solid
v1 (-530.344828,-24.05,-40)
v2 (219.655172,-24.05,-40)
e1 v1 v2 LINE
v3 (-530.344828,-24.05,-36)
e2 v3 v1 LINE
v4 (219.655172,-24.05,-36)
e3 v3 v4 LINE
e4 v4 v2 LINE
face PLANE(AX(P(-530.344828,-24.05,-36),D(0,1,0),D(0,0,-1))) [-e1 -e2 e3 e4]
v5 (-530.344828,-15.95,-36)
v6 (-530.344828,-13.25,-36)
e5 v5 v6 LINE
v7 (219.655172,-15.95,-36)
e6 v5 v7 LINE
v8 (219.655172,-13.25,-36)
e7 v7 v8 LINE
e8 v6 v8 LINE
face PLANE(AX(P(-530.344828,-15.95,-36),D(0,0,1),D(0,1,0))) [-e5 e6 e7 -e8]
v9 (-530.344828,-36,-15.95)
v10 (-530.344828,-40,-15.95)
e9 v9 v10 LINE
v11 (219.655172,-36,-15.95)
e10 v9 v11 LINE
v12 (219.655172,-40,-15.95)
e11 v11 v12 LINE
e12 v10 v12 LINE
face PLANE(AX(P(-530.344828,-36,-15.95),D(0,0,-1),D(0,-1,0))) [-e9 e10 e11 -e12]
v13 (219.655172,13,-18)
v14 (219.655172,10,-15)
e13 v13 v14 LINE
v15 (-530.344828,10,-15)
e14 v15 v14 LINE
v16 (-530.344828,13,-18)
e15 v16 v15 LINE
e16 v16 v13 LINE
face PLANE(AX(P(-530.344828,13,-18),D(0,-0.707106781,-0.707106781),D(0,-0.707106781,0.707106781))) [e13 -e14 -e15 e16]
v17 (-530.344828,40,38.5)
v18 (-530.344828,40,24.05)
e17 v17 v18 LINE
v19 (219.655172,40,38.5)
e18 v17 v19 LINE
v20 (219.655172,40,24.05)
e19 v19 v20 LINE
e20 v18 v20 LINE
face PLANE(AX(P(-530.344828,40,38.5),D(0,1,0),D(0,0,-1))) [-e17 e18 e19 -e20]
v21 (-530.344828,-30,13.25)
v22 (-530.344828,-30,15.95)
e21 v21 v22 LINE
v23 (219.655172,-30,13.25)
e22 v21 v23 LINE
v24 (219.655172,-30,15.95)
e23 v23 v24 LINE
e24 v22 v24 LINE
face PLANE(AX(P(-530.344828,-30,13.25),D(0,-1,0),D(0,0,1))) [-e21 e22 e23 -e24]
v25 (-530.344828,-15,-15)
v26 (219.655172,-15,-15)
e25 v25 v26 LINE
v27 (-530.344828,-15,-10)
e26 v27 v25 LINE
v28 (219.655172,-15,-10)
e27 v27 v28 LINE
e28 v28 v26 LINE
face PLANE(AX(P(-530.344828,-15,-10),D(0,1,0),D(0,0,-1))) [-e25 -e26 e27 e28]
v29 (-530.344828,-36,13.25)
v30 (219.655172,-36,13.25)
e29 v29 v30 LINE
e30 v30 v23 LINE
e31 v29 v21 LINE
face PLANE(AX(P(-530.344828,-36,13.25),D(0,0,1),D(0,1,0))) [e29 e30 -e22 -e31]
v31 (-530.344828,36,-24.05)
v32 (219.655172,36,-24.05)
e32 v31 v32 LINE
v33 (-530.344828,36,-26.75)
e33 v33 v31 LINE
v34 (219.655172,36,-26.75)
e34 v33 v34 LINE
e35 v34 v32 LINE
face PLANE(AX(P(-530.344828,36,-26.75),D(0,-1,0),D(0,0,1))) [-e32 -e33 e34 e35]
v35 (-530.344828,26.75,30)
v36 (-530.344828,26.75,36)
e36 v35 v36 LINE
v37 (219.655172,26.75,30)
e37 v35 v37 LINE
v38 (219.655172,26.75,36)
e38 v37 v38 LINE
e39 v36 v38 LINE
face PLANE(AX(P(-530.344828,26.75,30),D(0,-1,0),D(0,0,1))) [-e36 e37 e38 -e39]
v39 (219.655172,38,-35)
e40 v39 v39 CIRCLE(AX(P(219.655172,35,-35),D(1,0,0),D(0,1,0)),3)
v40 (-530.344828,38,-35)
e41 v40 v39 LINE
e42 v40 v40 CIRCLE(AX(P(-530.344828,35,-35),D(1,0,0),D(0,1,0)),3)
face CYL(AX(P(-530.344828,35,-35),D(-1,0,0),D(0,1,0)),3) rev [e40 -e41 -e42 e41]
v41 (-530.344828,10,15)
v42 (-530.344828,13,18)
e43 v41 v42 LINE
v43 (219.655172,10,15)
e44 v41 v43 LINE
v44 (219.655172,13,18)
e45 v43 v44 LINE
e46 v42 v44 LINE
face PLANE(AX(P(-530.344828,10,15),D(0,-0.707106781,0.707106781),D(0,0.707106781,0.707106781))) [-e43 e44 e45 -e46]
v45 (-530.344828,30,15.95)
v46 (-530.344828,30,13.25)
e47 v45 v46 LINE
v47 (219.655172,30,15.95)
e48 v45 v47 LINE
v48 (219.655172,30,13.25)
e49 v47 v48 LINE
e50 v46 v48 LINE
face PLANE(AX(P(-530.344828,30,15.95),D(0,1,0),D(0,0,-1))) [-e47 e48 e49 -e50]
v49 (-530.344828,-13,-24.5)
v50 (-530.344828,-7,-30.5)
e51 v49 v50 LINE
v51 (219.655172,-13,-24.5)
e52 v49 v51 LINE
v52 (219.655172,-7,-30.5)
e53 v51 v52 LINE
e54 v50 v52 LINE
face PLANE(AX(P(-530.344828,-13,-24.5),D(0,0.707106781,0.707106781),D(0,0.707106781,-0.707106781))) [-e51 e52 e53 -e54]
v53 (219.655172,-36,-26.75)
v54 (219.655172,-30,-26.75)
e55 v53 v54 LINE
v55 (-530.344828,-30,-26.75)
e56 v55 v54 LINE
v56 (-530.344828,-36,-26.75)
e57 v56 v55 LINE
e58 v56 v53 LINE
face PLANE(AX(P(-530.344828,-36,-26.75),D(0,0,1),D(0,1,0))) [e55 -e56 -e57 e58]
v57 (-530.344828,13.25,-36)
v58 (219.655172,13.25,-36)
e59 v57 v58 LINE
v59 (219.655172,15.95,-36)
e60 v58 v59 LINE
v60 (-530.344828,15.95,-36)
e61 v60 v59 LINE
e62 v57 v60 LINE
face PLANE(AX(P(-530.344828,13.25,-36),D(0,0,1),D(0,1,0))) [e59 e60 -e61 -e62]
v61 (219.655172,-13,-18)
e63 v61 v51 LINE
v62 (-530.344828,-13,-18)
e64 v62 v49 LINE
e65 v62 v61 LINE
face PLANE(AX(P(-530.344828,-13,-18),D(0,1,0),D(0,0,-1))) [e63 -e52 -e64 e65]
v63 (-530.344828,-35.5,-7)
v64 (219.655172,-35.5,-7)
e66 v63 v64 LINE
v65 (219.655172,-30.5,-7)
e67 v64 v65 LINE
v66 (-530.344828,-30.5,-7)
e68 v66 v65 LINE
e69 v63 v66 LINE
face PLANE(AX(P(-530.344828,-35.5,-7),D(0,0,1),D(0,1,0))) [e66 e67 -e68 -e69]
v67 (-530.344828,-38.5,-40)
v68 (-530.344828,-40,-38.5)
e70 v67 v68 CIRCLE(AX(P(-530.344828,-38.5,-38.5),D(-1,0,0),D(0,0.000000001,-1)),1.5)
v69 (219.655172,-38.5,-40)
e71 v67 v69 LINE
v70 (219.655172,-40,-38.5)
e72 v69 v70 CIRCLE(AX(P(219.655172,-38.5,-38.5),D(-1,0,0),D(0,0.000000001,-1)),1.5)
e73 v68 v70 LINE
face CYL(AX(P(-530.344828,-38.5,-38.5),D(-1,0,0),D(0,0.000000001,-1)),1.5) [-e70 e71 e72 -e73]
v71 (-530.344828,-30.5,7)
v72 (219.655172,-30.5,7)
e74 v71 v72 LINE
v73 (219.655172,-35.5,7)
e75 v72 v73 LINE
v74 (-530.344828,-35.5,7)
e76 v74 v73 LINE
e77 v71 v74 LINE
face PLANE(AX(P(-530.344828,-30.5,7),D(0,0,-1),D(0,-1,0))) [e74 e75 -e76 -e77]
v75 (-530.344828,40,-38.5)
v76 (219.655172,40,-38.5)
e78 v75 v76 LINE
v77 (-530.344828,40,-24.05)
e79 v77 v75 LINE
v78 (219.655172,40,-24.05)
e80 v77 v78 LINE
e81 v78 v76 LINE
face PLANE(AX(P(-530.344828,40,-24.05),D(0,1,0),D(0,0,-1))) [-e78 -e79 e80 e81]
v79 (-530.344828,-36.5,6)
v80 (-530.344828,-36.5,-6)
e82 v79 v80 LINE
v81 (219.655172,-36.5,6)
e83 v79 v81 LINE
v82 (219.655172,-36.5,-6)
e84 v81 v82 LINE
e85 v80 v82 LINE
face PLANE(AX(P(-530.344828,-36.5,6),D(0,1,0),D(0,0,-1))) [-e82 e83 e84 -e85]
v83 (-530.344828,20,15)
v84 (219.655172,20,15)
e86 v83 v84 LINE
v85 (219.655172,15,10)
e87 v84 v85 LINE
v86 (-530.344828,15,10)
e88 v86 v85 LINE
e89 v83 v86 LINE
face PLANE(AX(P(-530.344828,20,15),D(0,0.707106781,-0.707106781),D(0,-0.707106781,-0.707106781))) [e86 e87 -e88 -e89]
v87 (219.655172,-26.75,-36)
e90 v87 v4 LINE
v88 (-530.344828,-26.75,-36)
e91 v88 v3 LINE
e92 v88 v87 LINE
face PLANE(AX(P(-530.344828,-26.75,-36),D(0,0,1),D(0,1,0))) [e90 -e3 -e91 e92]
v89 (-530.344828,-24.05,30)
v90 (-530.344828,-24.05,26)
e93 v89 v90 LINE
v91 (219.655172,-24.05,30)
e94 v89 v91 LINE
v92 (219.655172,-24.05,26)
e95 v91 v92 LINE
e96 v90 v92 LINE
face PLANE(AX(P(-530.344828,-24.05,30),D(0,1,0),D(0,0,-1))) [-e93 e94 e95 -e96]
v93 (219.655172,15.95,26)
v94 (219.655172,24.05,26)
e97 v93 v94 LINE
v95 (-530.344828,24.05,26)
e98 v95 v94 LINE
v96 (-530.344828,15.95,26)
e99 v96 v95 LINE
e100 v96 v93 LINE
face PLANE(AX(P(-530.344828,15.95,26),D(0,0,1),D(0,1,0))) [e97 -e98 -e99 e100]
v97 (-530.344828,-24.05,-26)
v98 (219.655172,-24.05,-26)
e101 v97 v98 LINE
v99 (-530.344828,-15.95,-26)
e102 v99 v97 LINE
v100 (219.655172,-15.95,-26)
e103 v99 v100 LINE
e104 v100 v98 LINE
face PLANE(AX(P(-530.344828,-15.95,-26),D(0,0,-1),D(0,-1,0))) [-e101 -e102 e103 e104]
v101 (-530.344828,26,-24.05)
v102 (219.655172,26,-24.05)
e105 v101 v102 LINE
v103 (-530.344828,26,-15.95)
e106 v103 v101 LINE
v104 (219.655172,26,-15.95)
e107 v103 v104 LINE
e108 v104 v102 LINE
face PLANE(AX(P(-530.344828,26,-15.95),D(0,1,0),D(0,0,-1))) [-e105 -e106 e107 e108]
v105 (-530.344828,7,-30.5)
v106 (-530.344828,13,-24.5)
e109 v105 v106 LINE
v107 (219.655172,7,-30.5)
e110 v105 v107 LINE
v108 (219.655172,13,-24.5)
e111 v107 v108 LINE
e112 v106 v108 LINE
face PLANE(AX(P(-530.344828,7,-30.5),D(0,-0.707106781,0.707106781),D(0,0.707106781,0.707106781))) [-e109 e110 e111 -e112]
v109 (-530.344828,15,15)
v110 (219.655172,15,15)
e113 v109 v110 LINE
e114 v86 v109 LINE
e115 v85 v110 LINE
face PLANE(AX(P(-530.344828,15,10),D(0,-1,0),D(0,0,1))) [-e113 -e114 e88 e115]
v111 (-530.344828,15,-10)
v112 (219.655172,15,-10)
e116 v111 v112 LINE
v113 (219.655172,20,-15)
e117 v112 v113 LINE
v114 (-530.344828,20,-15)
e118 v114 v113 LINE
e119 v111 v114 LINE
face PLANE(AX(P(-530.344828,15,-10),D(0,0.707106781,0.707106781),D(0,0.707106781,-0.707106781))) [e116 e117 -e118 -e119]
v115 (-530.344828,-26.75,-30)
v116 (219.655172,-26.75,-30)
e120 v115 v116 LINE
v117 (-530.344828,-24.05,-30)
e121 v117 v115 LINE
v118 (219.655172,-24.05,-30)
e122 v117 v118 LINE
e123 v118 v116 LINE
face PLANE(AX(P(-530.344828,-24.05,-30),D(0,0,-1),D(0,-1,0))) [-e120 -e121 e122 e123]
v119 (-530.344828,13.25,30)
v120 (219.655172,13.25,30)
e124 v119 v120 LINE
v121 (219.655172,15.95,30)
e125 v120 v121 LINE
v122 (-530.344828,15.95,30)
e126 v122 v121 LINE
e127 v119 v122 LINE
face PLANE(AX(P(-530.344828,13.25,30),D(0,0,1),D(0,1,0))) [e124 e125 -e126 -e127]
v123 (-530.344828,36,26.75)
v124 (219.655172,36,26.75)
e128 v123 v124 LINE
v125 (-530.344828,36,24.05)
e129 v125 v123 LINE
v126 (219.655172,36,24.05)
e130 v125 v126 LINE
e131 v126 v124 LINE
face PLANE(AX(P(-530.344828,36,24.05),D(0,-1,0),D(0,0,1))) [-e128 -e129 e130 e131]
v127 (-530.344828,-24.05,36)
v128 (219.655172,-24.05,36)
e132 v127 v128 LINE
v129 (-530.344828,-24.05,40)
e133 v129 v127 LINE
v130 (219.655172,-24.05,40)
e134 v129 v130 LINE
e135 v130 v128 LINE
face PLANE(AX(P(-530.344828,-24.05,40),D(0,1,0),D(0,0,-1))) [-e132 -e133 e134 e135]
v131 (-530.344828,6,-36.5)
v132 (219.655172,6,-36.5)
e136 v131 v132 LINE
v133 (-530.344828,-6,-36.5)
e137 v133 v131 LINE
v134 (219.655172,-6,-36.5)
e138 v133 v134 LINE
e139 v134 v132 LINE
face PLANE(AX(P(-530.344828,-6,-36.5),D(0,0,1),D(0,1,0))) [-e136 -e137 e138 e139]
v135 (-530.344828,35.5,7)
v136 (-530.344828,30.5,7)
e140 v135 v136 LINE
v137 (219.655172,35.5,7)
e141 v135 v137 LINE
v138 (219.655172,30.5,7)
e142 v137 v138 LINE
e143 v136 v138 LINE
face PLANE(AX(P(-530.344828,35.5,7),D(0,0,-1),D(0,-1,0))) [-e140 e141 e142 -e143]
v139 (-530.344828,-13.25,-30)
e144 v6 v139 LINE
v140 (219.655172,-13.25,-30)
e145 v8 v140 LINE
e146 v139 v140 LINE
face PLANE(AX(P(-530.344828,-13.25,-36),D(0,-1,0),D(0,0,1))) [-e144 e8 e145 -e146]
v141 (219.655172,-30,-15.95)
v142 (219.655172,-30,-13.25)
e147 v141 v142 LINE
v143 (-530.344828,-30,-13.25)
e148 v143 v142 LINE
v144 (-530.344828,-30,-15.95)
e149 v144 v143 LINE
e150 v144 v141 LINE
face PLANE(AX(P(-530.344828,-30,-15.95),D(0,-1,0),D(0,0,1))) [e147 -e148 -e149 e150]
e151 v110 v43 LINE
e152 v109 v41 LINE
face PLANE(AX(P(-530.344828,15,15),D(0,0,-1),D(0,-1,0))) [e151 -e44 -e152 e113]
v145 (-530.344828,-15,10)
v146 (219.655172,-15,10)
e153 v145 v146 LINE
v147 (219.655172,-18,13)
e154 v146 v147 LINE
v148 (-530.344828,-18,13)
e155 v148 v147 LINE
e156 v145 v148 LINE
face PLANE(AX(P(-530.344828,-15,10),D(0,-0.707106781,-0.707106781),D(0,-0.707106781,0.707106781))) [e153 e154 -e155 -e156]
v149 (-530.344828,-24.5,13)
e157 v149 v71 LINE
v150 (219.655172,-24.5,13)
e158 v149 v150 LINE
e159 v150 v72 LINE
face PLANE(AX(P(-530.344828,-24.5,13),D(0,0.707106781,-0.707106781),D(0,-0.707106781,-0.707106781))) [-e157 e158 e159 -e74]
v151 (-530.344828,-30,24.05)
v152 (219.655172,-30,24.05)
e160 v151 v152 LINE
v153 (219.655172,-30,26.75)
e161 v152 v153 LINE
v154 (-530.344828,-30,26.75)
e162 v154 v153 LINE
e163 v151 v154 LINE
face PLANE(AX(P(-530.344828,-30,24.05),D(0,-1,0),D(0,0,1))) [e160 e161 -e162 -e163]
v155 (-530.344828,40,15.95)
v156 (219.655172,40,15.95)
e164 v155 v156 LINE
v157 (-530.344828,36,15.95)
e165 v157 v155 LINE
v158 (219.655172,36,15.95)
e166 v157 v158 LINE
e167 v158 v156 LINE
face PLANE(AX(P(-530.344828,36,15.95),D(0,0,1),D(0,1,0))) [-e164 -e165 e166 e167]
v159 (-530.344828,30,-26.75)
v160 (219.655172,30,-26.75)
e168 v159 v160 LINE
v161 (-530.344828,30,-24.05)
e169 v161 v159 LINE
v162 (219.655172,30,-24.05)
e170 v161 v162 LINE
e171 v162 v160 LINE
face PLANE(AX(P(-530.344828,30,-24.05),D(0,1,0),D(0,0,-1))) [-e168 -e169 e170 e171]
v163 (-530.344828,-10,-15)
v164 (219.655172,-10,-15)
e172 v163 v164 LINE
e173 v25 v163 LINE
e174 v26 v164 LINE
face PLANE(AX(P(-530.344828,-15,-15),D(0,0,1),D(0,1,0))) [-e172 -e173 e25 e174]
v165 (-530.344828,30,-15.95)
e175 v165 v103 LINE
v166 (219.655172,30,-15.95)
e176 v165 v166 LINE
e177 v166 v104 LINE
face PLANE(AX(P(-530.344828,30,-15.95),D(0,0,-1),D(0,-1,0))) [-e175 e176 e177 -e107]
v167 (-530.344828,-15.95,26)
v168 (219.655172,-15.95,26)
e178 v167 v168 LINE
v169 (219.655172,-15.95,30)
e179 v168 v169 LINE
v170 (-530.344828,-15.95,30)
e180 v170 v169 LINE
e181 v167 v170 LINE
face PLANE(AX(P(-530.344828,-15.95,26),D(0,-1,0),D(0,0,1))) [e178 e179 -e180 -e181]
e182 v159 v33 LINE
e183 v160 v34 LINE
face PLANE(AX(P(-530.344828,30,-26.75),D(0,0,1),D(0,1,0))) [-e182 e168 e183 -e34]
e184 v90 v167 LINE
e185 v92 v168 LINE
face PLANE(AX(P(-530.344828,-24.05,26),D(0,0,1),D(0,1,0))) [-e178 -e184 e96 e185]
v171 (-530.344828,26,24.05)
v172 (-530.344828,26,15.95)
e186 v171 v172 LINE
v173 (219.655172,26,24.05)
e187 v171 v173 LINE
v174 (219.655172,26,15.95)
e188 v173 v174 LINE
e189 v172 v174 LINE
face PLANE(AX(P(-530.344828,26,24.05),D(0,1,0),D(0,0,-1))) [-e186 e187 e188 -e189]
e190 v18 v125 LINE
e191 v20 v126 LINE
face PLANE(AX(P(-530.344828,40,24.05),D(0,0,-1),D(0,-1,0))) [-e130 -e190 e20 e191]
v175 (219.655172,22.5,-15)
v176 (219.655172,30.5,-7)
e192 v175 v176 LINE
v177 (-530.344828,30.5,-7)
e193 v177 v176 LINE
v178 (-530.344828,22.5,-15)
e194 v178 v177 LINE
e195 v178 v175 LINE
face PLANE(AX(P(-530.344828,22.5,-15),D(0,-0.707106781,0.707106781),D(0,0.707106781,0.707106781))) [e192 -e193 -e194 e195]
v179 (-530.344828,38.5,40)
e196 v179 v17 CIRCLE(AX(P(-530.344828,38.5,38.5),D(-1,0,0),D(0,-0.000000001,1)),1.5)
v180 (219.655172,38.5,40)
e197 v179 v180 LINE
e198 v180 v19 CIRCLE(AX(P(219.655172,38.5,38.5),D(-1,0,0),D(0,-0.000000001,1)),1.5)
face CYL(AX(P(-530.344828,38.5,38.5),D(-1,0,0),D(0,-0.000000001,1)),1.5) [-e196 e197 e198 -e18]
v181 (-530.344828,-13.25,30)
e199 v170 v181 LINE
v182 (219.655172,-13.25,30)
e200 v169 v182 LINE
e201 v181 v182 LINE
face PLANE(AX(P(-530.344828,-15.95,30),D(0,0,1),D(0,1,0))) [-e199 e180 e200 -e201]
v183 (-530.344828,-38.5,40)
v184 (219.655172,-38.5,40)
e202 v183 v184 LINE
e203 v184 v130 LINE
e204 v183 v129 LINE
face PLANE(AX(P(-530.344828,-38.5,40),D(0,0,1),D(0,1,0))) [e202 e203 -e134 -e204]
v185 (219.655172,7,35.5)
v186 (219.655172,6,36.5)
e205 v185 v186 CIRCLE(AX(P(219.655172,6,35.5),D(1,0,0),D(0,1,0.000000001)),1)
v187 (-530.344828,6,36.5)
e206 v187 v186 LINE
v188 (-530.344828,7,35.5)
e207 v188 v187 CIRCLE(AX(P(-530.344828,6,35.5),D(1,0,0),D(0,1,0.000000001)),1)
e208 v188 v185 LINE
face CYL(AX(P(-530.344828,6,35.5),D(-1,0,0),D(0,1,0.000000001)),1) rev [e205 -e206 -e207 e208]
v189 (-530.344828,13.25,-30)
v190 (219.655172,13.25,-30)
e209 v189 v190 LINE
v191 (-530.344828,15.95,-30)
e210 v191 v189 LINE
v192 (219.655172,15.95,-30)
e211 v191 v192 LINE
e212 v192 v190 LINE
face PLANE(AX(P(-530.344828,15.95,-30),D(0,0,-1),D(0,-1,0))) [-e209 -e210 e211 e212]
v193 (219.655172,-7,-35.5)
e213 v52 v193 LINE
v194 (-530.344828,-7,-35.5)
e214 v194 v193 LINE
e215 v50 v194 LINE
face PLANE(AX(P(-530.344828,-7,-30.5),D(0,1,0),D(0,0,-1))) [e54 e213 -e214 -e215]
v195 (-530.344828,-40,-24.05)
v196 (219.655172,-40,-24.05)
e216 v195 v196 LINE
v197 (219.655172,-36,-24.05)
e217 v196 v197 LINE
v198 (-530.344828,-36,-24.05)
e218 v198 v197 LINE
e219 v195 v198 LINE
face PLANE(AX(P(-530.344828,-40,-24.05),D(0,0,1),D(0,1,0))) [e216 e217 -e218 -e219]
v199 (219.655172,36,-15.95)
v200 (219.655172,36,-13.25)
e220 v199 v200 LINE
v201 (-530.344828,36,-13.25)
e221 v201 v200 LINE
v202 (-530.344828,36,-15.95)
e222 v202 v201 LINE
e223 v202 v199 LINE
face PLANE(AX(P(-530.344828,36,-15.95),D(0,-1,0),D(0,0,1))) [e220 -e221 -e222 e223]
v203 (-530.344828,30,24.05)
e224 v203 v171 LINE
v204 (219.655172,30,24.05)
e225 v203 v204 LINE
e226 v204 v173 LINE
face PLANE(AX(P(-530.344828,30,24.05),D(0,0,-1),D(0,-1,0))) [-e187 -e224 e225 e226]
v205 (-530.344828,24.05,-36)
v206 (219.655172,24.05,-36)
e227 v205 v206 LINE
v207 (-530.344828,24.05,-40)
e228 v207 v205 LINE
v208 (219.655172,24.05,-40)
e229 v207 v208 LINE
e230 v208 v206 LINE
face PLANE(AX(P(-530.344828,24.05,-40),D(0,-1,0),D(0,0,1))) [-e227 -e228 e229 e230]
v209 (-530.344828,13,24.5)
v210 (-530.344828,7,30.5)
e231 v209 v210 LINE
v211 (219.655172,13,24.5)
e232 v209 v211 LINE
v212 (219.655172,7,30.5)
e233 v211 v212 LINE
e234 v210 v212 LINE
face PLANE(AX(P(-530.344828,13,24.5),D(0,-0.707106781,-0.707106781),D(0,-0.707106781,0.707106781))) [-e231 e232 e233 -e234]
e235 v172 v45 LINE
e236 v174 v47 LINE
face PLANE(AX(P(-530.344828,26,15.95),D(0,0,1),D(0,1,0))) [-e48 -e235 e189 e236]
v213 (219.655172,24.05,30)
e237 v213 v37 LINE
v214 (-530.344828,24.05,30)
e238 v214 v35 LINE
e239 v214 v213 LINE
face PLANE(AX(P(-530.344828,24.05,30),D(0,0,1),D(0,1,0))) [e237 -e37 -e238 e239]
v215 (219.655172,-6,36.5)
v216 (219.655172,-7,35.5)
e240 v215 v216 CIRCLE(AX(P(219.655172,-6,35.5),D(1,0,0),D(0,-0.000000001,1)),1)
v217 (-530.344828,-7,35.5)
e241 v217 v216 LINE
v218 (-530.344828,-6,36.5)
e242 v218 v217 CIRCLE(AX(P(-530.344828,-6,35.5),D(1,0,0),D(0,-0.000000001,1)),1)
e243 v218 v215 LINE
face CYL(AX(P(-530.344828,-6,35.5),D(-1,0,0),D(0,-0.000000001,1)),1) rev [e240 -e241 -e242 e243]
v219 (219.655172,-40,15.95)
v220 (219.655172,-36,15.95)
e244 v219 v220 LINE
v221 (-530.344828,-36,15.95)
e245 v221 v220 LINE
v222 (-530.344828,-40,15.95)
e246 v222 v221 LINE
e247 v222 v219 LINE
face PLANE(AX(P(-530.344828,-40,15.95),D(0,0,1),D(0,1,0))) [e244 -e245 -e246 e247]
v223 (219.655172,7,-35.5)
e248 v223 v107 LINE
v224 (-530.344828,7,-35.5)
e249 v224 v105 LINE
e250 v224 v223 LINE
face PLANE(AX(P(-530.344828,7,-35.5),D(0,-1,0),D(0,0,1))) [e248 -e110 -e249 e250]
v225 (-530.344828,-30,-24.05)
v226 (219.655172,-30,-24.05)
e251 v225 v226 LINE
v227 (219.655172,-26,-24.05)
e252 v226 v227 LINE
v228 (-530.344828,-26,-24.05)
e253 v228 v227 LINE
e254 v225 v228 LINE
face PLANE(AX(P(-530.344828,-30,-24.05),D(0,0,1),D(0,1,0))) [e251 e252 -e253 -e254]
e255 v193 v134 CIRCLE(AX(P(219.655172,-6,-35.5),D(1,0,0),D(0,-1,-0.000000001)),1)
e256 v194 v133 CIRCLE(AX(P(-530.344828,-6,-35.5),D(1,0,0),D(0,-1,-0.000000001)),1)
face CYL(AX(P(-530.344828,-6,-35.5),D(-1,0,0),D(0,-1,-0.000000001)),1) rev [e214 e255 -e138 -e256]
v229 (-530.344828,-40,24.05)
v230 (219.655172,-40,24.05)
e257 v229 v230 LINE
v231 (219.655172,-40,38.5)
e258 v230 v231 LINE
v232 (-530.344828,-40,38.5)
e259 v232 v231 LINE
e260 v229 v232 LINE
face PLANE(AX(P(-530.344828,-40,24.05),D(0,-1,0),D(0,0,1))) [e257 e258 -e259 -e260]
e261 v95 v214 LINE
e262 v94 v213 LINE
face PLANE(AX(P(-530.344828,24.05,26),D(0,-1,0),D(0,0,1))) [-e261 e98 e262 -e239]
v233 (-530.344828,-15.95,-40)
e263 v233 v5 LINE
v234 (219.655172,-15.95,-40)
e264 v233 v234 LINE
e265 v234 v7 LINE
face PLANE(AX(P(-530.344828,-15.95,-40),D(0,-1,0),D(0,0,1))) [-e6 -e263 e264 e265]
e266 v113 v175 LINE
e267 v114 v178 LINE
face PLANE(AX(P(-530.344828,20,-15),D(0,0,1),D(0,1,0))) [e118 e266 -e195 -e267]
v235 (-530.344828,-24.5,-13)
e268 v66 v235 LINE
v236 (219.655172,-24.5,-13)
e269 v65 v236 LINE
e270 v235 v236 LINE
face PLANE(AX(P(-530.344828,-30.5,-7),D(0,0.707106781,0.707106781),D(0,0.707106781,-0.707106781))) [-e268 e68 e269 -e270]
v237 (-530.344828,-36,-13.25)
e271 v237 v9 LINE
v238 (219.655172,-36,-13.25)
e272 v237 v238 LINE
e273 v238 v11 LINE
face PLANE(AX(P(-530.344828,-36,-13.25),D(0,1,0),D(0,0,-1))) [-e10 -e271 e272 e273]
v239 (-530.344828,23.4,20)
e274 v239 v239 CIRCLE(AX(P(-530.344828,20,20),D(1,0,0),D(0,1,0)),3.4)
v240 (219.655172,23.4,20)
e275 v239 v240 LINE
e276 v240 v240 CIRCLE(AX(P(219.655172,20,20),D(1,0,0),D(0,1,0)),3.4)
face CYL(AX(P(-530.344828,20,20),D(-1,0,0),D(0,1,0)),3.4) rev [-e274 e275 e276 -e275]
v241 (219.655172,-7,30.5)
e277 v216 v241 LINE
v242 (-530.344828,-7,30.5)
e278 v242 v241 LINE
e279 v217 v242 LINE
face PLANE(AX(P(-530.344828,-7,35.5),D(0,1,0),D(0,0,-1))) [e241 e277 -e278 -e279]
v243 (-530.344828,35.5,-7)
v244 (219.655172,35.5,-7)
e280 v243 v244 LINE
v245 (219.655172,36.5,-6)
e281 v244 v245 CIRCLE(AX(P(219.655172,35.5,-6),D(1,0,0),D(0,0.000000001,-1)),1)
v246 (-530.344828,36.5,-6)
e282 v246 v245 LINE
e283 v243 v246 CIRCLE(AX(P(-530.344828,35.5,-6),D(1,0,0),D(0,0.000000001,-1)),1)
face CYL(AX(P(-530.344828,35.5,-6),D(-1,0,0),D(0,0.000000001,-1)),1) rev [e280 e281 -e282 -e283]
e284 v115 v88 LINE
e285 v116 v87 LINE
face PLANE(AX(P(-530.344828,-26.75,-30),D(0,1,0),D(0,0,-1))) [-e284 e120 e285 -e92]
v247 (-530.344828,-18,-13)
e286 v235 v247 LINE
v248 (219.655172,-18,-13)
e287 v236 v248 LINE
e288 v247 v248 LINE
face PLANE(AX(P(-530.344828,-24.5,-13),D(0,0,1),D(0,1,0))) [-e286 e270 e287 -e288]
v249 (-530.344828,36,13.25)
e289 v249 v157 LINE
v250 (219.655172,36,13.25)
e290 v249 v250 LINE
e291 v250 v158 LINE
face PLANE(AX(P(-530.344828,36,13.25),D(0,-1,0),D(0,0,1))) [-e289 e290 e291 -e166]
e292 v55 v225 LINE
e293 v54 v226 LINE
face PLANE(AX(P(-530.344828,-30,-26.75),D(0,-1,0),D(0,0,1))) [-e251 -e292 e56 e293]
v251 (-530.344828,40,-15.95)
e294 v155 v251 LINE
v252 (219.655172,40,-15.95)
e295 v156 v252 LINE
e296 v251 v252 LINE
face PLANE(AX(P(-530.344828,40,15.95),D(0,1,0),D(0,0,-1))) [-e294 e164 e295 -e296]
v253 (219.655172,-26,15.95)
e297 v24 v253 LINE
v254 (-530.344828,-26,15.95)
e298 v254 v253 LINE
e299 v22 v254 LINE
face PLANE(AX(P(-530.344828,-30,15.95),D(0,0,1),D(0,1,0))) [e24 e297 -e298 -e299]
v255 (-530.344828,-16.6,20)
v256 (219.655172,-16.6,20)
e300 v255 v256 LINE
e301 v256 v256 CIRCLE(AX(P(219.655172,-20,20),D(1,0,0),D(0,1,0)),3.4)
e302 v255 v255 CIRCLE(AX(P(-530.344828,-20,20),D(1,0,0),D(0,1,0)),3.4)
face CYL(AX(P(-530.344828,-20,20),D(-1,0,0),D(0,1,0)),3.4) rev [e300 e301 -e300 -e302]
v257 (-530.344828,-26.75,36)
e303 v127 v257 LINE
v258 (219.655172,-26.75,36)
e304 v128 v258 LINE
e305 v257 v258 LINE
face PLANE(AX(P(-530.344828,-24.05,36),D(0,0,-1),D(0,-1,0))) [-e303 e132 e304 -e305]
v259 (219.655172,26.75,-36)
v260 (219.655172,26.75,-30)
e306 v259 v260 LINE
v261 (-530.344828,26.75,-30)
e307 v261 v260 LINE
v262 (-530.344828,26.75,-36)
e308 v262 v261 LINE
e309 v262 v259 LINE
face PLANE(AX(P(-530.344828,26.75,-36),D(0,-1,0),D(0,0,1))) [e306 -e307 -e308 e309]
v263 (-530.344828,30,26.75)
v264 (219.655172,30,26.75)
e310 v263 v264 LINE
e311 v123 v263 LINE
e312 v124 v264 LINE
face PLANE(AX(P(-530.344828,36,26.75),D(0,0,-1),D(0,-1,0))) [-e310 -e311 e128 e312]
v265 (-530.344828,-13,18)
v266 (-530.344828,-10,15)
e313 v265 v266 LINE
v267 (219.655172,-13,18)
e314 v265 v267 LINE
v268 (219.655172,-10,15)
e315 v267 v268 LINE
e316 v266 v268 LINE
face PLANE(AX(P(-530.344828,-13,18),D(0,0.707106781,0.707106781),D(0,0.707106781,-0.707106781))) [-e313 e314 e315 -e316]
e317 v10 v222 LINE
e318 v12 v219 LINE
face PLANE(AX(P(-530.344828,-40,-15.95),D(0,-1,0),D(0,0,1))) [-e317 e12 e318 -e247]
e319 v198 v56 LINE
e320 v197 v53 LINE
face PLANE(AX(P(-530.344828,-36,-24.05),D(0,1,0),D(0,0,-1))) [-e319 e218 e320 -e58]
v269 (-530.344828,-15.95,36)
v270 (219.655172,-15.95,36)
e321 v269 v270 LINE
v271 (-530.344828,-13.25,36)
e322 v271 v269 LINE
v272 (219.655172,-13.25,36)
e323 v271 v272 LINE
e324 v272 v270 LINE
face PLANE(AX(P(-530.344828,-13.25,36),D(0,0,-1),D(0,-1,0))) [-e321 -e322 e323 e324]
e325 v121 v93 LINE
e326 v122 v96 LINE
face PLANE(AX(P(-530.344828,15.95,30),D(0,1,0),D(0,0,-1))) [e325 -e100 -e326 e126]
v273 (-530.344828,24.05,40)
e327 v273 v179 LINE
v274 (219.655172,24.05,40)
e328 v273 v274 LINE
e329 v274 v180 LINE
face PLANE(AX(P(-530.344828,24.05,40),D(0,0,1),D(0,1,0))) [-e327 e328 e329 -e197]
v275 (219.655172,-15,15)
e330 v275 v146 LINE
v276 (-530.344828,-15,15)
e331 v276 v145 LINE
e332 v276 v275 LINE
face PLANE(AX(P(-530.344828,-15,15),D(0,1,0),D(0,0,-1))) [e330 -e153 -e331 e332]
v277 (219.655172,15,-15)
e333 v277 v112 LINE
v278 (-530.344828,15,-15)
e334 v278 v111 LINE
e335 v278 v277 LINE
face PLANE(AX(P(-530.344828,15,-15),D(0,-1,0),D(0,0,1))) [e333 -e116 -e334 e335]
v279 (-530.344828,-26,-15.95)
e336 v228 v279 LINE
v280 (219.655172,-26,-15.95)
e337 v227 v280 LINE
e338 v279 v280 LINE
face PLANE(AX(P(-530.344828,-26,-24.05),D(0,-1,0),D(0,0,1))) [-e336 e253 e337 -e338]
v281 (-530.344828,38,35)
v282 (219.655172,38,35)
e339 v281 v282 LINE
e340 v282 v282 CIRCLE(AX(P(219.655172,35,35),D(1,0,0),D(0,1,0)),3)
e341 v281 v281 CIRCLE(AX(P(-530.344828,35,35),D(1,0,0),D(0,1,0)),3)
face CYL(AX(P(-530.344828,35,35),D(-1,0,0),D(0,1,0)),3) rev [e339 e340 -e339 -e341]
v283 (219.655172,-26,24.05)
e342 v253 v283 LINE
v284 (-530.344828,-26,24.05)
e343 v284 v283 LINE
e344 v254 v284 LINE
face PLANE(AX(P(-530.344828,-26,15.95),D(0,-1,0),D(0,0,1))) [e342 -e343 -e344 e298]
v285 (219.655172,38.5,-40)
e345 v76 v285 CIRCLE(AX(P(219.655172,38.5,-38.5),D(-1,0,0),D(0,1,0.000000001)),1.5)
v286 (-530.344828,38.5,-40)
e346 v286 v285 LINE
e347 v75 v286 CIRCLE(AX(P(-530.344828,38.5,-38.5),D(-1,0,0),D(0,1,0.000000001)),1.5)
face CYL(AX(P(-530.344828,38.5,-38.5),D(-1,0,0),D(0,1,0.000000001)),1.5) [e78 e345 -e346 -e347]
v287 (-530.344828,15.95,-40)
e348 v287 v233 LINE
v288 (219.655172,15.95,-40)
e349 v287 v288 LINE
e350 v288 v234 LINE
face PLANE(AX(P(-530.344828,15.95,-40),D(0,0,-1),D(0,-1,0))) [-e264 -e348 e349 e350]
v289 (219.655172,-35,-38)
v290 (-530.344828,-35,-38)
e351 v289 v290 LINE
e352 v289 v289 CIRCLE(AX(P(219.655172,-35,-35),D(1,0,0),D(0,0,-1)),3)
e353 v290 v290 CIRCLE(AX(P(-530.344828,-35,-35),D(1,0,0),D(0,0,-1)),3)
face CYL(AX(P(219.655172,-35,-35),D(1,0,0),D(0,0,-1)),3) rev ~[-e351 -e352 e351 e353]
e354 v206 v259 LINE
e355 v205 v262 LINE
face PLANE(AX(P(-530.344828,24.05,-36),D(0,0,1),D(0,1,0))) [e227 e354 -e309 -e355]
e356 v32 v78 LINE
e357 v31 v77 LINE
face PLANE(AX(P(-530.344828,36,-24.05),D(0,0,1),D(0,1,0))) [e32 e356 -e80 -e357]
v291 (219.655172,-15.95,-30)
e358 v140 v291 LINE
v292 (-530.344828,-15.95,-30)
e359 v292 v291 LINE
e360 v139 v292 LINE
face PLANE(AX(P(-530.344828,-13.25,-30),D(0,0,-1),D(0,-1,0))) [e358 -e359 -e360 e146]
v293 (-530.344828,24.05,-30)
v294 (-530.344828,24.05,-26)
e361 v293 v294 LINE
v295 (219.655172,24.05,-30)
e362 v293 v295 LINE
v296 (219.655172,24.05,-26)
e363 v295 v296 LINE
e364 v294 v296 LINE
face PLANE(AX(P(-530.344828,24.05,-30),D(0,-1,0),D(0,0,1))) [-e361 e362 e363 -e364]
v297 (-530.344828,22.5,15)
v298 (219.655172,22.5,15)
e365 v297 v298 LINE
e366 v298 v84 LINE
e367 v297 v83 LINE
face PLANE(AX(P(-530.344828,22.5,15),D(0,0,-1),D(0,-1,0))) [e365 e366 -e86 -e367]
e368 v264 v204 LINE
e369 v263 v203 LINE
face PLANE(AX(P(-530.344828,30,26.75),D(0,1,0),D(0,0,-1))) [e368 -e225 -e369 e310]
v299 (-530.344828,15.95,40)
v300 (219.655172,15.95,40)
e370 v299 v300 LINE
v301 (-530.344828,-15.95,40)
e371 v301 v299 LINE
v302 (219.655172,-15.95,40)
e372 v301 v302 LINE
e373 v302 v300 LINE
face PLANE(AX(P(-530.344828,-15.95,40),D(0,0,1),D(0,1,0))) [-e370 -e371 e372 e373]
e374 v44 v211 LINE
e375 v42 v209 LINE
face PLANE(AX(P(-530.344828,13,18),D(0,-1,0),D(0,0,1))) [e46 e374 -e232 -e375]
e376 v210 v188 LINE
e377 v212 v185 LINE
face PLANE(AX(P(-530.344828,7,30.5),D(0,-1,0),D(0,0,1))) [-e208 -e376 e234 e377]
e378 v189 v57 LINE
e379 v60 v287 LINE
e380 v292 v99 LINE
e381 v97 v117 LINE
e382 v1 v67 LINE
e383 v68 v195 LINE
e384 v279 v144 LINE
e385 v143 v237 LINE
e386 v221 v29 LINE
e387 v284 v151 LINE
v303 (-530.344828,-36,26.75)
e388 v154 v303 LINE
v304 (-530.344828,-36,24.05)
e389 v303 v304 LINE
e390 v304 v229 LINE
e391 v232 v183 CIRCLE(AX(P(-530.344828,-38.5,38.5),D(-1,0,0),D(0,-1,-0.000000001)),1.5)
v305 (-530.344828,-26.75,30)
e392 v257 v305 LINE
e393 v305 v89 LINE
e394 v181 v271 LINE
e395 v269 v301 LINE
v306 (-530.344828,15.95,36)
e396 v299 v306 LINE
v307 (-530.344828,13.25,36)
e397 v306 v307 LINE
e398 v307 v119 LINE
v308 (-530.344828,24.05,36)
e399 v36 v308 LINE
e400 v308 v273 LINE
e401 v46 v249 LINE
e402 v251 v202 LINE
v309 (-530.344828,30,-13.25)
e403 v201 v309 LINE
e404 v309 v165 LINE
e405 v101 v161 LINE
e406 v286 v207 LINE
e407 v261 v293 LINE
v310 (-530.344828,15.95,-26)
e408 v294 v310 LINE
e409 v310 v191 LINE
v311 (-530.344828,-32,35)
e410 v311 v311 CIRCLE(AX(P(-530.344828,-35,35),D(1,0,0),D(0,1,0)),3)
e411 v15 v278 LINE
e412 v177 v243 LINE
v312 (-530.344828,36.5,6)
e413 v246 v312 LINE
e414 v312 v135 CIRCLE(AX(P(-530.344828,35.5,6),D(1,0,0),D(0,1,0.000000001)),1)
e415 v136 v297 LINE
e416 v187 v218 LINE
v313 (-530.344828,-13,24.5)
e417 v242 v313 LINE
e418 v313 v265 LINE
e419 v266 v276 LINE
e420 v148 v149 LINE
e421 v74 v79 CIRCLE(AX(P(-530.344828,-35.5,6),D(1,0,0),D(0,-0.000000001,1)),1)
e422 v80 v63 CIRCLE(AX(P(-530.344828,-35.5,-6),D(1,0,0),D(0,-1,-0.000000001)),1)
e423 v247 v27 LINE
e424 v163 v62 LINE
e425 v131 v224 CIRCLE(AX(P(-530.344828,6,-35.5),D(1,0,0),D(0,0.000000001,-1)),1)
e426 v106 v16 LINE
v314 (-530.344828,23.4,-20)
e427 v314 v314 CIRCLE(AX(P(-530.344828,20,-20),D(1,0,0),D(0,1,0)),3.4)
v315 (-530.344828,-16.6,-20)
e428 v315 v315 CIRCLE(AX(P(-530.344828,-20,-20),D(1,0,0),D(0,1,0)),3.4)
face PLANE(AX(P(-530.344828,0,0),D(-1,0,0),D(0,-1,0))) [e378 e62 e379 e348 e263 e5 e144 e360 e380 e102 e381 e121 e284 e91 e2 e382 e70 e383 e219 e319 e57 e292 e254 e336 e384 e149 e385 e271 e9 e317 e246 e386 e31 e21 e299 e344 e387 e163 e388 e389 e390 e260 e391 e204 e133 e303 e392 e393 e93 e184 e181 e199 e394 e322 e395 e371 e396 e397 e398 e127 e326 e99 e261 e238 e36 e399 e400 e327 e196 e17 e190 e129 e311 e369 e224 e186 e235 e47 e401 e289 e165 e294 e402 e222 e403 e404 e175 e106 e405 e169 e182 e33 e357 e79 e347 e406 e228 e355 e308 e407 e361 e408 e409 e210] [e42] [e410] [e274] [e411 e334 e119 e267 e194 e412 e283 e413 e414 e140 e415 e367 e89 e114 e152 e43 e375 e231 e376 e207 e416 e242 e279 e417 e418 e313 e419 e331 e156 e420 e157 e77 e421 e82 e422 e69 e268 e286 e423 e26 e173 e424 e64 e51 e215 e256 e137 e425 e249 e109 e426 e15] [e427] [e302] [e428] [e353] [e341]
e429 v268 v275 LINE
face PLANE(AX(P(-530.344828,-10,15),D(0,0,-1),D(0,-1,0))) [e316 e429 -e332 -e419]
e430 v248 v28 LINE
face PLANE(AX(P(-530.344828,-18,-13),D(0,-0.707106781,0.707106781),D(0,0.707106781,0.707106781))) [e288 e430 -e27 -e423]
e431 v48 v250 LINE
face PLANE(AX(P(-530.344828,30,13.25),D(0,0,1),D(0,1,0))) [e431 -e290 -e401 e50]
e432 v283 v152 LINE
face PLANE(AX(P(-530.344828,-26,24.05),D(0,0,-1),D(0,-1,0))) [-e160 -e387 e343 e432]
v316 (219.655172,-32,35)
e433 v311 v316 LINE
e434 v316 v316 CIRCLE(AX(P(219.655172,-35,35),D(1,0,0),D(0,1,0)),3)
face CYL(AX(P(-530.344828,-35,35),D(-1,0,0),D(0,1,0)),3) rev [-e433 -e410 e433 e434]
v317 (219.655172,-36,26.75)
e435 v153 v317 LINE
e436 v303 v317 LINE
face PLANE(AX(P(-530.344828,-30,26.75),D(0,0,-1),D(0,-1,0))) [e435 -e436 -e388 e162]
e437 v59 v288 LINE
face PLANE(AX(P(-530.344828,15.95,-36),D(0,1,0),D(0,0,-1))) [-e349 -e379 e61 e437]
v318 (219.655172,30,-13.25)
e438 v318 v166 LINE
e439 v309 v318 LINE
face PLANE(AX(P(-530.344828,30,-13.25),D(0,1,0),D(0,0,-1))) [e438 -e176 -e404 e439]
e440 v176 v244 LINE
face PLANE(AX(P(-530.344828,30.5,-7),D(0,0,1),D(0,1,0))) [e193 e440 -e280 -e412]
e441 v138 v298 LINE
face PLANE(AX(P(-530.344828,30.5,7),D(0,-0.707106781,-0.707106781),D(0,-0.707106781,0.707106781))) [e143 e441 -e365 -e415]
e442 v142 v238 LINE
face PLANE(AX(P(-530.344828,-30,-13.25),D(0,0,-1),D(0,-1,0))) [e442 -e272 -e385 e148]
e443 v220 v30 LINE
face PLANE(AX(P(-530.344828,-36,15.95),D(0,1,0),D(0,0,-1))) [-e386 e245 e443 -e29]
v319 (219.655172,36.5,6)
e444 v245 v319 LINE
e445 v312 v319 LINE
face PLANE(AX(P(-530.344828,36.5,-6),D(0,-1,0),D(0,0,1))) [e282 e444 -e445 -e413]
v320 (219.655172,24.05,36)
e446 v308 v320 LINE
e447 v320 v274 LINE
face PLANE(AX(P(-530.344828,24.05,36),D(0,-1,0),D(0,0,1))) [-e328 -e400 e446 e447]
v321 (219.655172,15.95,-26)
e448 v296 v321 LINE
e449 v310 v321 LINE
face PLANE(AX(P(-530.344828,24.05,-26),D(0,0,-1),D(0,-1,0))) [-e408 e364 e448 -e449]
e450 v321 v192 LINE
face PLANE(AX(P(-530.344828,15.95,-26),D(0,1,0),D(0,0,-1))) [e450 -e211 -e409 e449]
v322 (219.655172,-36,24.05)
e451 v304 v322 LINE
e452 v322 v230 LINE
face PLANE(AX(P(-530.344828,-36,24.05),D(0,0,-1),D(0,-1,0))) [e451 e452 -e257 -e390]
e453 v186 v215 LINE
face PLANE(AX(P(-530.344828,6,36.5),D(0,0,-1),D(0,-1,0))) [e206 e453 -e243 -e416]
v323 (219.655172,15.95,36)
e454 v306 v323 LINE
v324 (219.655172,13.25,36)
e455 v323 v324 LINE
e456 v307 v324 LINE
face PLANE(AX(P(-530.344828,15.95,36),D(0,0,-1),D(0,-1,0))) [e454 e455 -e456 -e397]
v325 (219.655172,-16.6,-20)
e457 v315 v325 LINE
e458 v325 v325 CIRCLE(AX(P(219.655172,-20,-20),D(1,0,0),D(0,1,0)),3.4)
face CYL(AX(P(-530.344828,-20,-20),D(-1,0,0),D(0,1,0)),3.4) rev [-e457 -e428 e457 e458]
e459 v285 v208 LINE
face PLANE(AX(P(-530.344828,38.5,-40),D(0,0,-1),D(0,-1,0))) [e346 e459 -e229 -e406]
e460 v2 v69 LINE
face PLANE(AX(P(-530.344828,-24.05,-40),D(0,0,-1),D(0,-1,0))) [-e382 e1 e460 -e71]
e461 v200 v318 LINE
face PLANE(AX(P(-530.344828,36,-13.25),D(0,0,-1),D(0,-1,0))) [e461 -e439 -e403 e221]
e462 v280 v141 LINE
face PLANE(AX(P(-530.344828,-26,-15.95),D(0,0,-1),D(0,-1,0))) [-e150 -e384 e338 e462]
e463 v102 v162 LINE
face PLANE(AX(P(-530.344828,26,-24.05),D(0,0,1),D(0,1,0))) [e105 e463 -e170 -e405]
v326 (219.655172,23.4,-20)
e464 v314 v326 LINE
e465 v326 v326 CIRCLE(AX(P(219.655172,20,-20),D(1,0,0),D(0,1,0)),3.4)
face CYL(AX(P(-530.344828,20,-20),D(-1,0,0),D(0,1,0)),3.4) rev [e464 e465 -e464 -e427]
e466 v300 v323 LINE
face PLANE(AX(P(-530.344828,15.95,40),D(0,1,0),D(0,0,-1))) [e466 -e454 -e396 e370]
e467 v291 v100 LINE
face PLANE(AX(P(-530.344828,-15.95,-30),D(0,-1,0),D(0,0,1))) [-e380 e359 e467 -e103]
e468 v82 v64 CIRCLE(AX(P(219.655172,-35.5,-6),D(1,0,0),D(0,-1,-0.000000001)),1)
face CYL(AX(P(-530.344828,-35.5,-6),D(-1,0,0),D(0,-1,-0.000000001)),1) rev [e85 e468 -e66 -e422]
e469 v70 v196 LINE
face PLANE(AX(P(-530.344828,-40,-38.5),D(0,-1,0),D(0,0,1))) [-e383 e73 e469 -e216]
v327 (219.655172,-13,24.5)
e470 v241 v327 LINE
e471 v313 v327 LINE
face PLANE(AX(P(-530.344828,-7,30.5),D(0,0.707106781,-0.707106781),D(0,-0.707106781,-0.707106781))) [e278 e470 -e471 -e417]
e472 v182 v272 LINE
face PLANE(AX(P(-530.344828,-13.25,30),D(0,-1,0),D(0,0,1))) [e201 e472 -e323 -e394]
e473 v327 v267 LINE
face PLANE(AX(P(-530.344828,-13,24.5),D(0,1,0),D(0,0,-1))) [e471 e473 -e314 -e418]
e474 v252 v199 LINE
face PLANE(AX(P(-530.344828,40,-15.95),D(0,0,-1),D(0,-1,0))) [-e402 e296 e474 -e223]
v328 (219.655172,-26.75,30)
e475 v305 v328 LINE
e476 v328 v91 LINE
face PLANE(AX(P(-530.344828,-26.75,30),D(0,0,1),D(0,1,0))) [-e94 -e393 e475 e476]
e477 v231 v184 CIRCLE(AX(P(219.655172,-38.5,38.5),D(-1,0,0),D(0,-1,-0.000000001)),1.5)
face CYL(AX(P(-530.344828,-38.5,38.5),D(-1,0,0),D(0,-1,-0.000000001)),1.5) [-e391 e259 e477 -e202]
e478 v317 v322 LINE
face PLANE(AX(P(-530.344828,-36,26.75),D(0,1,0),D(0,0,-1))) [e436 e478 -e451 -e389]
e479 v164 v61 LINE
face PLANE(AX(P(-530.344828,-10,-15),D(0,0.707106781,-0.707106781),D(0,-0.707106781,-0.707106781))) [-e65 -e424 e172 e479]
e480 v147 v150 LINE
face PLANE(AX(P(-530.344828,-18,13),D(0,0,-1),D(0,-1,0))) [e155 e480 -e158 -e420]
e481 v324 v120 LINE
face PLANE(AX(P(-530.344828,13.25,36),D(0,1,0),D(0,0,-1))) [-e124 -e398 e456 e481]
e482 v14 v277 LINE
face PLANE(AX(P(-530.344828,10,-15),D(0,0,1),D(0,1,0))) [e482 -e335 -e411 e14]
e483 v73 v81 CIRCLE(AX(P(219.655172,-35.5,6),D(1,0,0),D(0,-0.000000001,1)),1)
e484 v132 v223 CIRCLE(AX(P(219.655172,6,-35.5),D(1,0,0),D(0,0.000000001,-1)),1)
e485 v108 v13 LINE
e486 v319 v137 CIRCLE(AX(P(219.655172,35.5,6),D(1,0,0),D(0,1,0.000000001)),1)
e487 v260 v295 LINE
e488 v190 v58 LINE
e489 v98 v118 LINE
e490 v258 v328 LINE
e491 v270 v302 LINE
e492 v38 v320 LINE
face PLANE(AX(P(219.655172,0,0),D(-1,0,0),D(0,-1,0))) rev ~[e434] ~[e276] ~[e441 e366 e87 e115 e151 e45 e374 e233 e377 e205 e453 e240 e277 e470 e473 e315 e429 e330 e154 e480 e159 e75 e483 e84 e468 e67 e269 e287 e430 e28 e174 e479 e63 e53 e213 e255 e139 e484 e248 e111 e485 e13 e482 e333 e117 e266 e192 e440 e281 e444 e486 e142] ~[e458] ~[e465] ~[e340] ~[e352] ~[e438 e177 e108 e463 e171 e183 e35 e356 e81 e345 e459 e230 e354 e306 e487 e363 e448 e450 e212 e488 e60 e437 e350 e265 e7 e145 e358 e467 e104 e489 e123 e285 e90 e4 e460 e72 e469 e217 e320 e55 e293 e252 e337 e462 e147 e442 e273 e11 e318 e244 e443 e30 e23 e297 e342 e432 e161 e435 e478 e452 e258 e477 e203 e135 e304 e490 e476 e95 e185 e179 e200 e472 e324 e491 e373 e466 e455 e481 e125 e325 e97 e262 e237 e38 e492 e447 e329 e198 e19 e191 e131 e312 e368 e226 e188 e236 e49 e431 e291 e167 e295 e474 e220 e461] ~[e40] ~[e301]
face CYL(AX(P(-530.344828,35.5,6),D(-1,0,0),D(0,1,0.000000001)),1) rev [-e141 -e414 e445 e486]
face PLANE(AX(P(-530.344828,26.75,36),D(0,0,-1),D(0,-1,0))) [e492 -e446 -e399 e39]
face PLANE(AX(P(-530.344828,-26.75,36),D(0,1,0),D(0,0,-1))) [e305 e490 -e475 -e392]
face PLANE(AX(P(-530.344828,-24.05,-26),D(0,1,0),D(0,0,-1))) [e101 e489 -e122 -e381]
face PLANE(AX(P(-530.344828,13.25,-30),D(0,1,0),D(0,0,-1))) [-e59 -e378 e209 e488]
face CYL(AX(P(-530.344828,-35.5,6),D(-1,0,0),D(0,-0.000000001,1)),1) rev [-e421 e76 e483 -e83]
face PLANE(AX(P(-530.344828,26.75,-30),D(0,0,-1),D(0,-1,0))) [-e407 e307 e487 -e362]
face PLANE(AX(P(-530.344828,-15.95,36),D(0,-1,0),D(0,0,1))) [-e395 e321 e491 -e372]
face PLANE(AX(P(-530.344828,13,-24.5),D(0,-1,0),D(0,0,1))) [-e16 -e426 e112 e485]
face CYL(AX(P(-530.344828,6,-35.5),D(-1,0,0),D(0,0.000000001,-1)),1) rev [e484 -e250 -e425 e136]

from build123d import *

# Parameters (mm, degrees)
SKETCH1_R                                 = 3.4
SKETCH1_R_2                               = 3
ALUMINIUM_PROFILE_80_X_80G_X_R1_5_1_DEPTH = 750
SKETCH10_R                                = 3
CUT_EXTRUDE1_DEPTH                        = 753.130307859


with BuildPart() as part:
    # Sketch1 → Aluminium profile 80 X 80G X R1.5(1) (new body)
    with BuildSketch(Plane.YZ.offset(-530.344827586)):
        with BuildLine():
            Line((-24.05, 40), (-24.05, 36))
            Line((-24.05, 36), (-26.75, 36))
            Line((-26.75, 36), (-26.75, 30))
            Line((-26.75, 30), (-24.05, 30))
            Line((-24.05, 30), (-24.05, 26))
            Line((-24.05, 26), (-15.95, 26))
            Line((-15.95, 26), (-15.95, 30))
            Line((-15.95, 30), (-13.25, 30))
            Line((-13.25, 30), (-13.25, 36))
            Line((-13.25, 36), (-15.95, 36))
            Line((-15.95, 36), (-15.95, 40))
            Line((-15.95, 40), (15.95, 40))
            Line((15.95, 40), (15.95, 36))
            Line((15.95, 36), (13.25, 36))
            Line((13.25, 36), (13.25, 30))
            Line((13.25, 30), (15.95, 30))
            Line((15.95, 30), (15.95, 26))
            Line((15.95, 26), (24.05, 26))
            Line((24.05, 26), (24.05, 30))
            Line((24.05, 30), (26.75, 30))
            Line((26.75, 30), (26.75, 36))
            Line((26.75, 36), (24.05, 36))
            Line((24.05, 36), (24.05, 40))
            Line((24.05, 40), (38.5, 40))
            ThreePointArc((38.5, 40), (39.560660172, 39.560660172), (40, 38.5))
            Line((40, 38.5), (40, 24.05))
            Line((40, 24.05), (36, 24.05))
            Line((36, 24.05), (36, 26.75))
            Line((36, 26.75), (30, 26.75))
            Line((30, 26.75), (30, 24.05))
            Line((30, 24.05), (26, 24.05))
            Line((26, 24.05), (26, 15.95))
            Line((26, 15.95), (30, 15.95))
            Line((30, 15.95), (30, 13.25))
            Line((30, 13.25), (36, 13.25))
            Line((36, 13.25), (36, 15.95))
            Line((36, 15.95), (40, 15.95))
            Line((40, 15.95), (40, -15.95))
            Line((40, -15.95), (36, -15.95))
            Line((36, -15.95), (36, -13.25))
            Line((36, -13.25), (30, -13.25))
            Line((30, -13.25), (30, -15.95))
            Line((30, -15.95), (26, -15.95))
            Line((26, -15.95), (26, -24.05))
            Line((26, -24.05), (30, -24.05))
            Line((30, -24.05), (30, -26.75))
            Line((30, -26.75), (36, -26.75))
            Line((36, -26.75), (36, -24.05))
            Line((36, -24.05), (40, -24.05))
            Line((40, -24.05), (40, -38.5))
            ThreePointArc((40, -38.5), (39.560660172, -39.560660172), (38.5, -40))
            Line((38.5, -40), (24.05, -40))
            Line((24.05, -40), (24.05, -36))
            Line((24.05, -36), (26.75, -36))
            Line((26.75, -36), (26.75, -30))
            Line((26.75, -30), (24.05, -30))
            Line((24.05, -30), (24.05, -26))
            Line((24.05, -26), (15.95, -26))
            Line((15.95, -26), (15.95, -30))
            Line((15.95, -30), (13.25, -30))
            Line((13.25, -30), (13.25, -36))
            Line((13.25, -36), (15.95, -36))
            Line((15.95, -36), (15.95, -40))
            Line((15.95, -40), (-15.95, -40))
            Line((-15.95, -40), (-15.95, -36))
            Line((-15.95, -36), (-13.25, -36))
            Line((-13.25, -36), (-13.25, -30))
            Line((-13.25, -30), (-15.95, -30))
            Line((-15.95, -30), (-15.95, -26))
            Line((-15.95, -26), (-24.05, -26))
            Line((-24.05, -26), (-24.05, -30))
            Line((-24.05, -30), (-26.75, -30))
            Line((-26.75, -30), (-26.75, -36))
            Line((-26.75, -36), (-24.05, -36))
            Line((-24.05, -36), (-24.05, -40))
            Line((-24.05, -40), (-38.5, -40))
            ThreePointArc((-38.5, -40), (-39.560660172, -39.560660172), (-40, -38.5))
            Line((-40, -38.5), (-40, -24.05))
            Line((-40, -24.05), (-36, -24.05))
            Line((-36, -24.05), (-36, -26.75))
            Line((-36, -26.75), (-30, -26.75))
            Line((-30, -26.75), (-30, -24.05))
            Line((-30, -24.05), (-26, -24.05))
            Line((-26, -24.05), (-26, -15.95))
            Line((-26, -15.95), (-30, -15.95))
            Line((-30, -15.95), (-30, -13.25))
            Line((-30, -13.25), (-36, -13.25))
            Line((-36, -13.25), (-36, -15.95))
            Line((-36, -15.95), (-40, -15.95))
            Line((-40, -15.95), (-40, 15.95))
            Line((-40, 15.95), (-36, 15.95))
            Line((-36, 15.95), (-36, 13.25))
            Line((-36, 13.25), (-30, 13.25))
            Line((-30, 13.25), (-30, 15.95))
            Line((-30, 15.95), (-26, 15.95))
            Line((-26, 15.95), (-26, 24.05))
            Line((-26, 24.05), (-30, 24.05))
            Line((-30, 24.05), (-30, 26.75))
            Line((-30, 26.75), (-36, 26.75))
            Line((-36, 26.75), (-36, 24.05))
            Line((-36, 24.05), (-40, 24.05))
            Line((-40, 24.05), (-40, 38.5))
            ThreePointArc((-40, 38.5), (-39.560660172, 39.560660172), (-38.5, 40))
            Line((-38.5, 40), (-24.05, 40))
        make_face()
        with Locations((-20, 20)):
            Circle(SKETCH1_R, mode=Mode.SUBTRACT)
        with Locations((20, 20)):
            Circle(SKETCH1_R, mode=Mode.SUBTRACT)
        with Locations((20, -20)):
            Circle(SKETCH1_R, mode=Mode.SUBTRACT)
        with Locations((-20, -20)):
            Circle(SKETCH1_R, mode=Mode.SUBTRACT)
        with Locations((-35, 35)):
            Circle(SKETCH1_R_2, mode=Mode.SUBTRACT)
        with Locations((35, 35)):
            Circle(SKETCH1_R_2, mode=Mode.SUBTRACT)
        with Locations((35, -35)):
            Circle(SKETCH1_R_2, mode=Mode.SUBTRACT)
        with BuildLine():
            Line((-13, 18), (-10, 15))
            Line((-10, 15), (-15, 15))
            Line((-15, 15), (-15, 10))
            Line((-15, 10), (-18, 13))
            Line((-18, 13), (-24.5, 13))
            Line((-24.5, 13), (-30.5, 7))
            Line((-30.5, 7), (-35.5, 7))
            ThreePointArc((-35.5, 7), (-36.207106781, 6.707106781), (-36.5, 6))
            Line((-36.5, 6), (-36.5, -6))
            ThreePointArc((-36.5, -6), (-36.207106781, -6.707106781), (-35.5, -7))
            Line((-35.5, -7), (-30.5, -7))
            Line((-30.5, -7), (-24.5, -13))
            Line((-24.5, -13), (-18, -13))
            Line((-18, -13), (-15, -10))
            Line((-15, -10), (-15, -15))
            Line((-15, -15), (-10, -15))
            Line((-10, -15), (-13, -18))
            Line((-13, -18), (-13, -24.5))
            Line((-13, -24.5), (-7, -30.5))
            Line((-7, -30.5), (-7, -35.5))
            ThreePointArc((-7, -35.5), (-6.707106781, -36.207106781), (-6, -36.5))
            Line((-6, -36.5), (6, -36.5))
            ThreePointArc((6, -36.5), (6.707106781, -36.207106781), (7, -35.5))
            Line((7, -35.5), (7, -30.5))
            Line((7, -30.5), (13, -24.5))
            Line((13, -24.5), (13, -18))
            Line((13, -18), (10, -15))
            Line((10, -15), (15, -15))
            Line((15, -15), (15, -10))
            Line((15, -10), (20, -15))
            Line((20, -15), (22.5, -15))
            Line((22.5, -15), (30.5, -7))
            Line((30.5, -7), (35.5, -7))
            ThreePointArc((35.5, -7), (36.207106781, -6.707106781), (36.5, -6))
            Line((36.5, -6), (36.5, 6))
            ThreePointArc((36.5, 6), (36.207106781, 6.707106781), (35.5, 7))
            Line((35.5, 7), (30.5, 7))
            Line((30.5, 7), (22.5, 15))
            Line((22.5, 15), (20, 15))
            Line((20, 15), (15, 10))
            Line((15, 10), (15, 15))
            Line((15, 15), (10, 15))
            Line((10, 15), (13, 18))
            Line((13, 18), (13, 24.5))
            Line((13, 24.5), (7, 30.5))
            Line((7, 30.5), (7, 35.5))
            ThreePointArc((7, 35.5), (6.707106781, 36.207106781), (6, 36.5))
            Line((6, 36.5), (-6, 36.5))
            ThreePointArc((-6, 36.5), (-6.707106781, 36.207106781), (-7, 35.5))
            Line((-7, 35.5), (-7, 30.5))
            Line((-7, 30.5), (-13, 24.5))
            Line((-13, 24.5), (-13, 18))
        make_face(mode=Mode.SUBTRACT)
    extrude(amount=ALUMINIUM_PROFILE_80_X_80G_X_R1_5_1_DEPTH)

    # Sketch10 → Cut-Extrude1 (cut, through all)
    with BuildSketch(Plane(origin=(219.655172414, 0, 0), x_dir=(0, 0, -1), z_dir=(1, 0, 0))):
        with Locations((35, -35)):
            Circle(SKETCH10_R)
    extrude(amount=-CUT_EXTRUDE1_DEPTH, mode=Mode.SUBTRACT)


solid = part.part
